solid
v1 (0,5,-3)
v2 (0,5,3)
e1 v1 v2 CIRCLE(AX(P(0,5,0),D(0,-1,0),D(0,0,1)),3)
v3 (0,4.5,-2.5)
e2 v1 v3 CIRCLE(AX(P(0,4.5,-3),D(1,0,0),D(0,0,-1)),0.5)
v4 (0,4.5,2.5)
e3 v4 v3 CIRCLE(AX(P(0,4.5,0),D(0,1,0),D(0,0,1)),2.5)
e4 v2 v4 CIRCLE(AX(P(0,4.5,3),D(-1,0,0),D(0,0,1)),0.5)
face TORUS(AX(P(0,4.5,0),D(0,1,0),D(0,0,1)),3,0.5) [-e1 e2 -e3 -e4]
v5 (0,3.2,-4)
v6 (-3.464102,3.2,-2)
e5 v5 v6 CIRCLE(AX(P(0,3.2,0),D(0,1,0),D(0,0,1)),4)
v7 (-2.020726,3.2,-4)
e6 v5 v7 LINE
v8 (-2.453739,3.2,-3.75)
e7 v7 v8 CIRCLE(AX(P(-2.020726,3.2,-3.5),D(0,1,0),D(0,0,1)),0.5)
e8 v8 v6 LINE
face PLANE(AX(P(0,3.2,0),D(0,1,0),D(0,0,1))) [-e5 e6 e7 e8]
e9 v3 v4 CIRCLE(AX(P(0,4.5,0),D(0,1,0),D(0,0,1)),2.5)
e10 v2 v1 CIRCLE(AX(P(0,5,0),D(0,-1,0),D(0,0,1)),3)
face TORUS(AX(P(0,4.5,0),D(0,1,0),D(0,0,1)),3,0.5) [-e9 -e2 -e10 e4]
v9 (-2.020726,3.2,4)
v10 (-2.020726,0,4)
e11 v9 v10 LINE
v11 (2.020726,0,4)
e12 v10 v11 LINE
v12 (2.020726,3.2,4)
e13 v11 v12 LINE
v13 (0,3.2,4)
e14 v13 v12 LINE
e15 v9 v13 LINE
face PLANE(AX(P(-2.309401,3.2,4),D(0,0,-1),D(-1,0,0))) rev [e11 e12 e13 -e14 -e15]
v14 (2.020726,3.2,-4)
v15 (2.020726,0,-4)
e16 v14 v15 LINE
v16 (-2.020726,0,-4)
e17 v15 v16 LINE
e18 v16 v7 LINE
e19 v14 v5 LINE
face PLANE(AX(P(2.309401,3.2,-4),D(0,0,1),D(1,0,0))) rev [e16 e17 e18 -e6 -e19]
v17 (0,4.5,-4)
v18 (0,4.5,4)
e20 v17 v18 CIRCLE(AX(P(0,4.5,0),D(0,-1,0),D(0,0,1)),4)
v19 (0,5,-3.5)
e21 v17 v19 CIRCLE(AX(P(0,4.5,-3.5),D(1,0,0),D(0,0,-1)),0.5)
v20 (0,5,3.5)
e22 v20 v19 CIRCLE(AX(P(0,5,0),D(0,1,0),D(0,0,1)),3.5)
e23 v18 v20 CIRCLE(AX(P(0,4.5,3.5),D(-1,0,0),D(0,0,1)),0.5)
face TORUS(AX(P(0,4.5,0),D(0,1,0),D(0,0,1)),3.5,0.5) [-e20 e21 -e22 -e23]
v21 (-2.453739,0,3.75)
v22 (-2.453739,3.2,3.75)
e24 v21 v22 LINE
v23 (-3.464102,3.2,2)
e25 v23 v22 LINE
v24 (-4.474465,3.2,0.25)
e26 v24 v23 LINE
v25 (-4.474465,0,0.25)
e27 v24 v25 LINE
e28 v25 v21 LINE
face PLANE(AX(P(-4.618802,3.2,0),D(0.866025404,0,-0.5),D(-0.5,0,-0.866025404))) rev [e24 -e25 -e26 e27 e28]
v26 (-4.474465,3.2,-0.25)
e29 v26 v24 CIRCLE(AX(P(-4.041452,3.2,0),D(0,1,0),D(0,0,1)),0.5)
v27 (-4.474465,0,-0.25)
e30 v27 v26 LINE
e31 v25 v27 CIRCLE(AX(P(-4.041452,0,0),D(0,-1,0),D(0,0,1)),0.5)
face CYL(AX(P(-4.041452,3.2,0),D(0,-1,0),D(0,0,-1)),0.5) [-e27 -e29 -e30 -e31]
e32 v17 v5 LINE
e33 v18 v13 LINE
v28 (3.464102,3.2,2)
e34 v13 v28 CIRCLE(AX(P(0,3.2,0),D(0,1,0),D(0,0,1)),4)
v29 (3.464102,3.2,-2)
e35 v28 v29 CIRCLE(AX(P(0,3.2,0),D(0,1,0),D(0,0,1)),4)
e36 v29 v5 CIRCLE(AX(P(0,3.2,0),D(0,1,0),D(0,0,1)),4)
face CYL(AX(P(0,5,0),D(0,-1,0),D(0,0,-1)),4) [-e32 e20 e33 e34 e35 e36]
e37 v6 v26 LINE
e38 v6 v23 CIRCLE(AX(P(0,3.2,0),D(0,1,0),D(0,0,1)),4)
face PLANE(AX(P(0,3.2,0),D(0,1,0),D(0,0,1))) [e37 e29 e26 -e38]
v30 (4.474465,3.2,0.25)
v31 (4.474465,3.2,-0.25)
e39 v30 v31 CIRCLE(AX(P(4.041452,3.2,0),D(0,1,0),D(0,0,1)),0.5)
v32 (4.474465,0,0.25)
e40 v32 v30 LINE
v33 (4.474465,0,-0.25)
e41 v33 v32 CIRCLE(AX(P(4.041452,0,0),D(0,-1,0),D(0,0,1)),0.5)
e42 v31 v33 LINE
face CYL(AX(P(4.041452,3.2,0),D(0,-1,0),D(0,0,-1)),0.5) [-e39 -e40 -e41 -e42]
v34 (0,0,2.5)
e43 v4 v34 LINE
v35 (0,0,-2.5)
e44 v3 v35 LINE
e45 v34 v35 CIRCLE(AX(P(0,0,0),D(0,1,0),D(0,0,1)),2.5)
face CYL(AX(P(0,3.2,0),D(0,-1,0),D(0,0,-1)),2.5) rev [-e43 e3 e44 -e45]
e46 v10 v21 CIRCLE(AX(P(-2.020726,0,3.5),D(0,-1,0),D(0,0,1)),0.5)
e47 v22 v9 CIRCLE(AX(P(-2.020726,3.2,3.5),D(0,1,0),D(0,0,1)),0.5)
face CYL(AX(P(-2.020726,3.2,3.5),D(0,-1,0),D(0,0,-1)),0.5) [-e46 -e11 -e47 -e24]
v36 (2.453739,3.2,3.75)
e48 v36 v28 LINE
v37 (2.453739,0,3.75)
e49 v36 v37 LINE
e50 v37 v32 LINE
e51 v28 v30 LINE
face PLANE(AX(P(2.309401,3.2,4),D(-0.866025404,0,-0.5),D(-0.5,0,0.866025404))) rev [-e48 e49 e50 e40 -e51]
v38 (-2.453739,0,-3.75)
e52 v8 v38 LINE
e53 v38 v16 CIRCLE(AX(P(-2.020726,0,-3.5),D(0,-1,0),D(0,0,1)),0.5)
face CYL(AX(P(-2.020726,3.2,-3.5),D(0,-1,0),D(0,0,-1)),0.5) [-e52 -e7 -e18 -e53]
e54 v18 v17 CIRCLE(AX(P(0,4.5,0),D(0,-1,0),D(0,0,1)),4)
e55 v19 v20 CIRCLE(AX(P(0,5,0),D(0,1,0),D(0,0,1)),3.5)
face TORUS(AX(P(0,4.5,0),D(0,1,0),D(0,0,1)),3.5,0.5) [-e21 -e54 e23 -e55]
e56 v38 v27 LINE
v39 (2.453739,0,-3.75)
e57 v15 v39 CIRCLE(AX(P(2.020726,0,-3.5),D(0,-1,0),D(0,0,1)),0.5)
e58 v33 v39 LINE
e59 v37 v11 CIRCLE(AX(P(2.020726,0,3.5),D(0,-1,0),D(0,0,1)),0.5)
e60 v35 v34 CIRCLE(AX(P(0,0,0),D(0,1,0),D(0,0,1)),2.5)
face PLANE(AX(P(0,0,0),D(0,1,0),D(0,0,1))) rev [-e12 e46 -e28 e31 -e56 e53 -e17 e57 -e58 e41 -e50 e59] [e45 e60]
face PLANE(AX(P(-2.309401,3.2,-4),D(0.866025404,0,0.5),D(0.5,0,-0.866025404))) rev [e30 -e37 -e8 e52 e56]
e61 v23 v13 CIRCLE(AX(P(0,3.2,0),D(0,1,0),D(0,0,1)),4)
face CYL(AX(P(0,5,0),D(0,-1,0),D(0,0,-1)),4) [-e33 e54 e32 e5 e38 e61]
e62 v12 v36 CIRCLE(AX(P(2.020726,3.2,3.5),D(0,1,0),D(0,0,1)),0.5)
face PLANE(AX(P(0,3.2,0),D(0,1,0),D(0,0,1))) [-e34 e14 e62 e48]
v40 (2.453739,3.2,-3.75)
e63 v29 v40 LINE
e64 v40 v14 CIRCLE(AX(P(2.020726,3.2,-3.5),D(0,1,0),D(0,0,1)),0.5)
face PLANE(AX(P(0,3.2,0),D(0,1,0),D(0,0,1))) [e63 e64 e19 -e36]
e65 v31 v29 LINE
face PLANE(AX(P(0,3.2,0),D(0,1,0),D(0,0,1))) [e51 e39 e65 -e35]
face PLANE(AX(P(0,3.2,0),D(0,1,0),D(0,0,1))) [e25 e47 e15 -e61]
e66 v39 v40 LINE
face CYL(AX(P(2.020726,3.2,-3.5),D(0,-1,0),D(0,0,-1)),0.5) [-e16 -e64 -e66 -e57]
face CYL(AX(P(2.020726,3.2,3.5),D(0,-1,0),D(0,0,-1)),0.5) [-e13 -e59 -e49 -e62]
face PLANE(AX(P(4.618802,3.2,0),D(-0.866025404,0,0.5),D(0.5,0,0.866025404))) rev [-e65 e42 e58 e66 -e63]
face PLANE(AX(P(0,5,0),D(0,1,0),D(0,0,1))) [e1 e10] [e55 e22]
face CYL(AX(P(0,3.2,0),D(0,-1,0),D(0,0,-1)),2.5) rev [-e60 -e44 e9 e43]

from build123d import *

# Parameters (mm, degrees)
SKETCH_1_R      = 2.5
EXTRUDE_1_DEPTH = 3.2
SKETCH_2_R      = 4
SKETCH_2_R_2    = 2.5
EXTRUDE_2_DEPTH = 1.8
FILLET_3_R      = 0.5


with BuildPart() as part:
    # 草图1 → 凸台-拉伸1 (new body)
    with BuildSketch(Plane(origin=(0, 0, 0), x_dir=(1, 0, 0), z_dir=(0, 1, 0))):
        Polygon((4.618802154, 0), (2.309401077, 4), (-2.309401077, 4), (-4.618802154, 0), (-2.309401077, -4), (2.309401077, -4), align=None)
        with Locations(Location((0, 0, 0), (0, 0, 270))):
            Circle(SKETCH_1_R, mode=Mode.SUBTRACT)
    extrude(amount=EXTRUDE_1_DEPTH)

    # 草图2 → 凸台-拉伸2 (add)
    with BuildSketch(Plane(origin=(0, 3.2, 0), x_dir=(1, 0, 0), z_dir=(0, 1, 0))):
        with Locations(Location((0, 0, 0), (0, 0, 270))):
            Circle(SKETCH_2_R)
        with Locations(Location((0, 0, 0), (0, 0, 270))):
            Circle(SKETCH_2_R_2, mode=Mode.SUBTRACT)
    extrude(amount=EXTRUDE_2_DEPTH)

    # 圆角3
    fillet_3_edges = [part.edges().sort_by_distance(p)[0] for p in [
        (2.309401077, 1.6, 4),
        (-2.309401077, 1.6, 4),
        (-4.618802154, 1.6, 0),
        (-2.309401077, 1.6, -4),
        (2.309401077, 1.6, -4),
        (4.618802154, 1.6, 0),
        (0, 5, -4),
        (0, 5, -2.5),
    ]]
    fillet(fillet_3_edges, radius=FILLET_3_R)


solid = part.part
